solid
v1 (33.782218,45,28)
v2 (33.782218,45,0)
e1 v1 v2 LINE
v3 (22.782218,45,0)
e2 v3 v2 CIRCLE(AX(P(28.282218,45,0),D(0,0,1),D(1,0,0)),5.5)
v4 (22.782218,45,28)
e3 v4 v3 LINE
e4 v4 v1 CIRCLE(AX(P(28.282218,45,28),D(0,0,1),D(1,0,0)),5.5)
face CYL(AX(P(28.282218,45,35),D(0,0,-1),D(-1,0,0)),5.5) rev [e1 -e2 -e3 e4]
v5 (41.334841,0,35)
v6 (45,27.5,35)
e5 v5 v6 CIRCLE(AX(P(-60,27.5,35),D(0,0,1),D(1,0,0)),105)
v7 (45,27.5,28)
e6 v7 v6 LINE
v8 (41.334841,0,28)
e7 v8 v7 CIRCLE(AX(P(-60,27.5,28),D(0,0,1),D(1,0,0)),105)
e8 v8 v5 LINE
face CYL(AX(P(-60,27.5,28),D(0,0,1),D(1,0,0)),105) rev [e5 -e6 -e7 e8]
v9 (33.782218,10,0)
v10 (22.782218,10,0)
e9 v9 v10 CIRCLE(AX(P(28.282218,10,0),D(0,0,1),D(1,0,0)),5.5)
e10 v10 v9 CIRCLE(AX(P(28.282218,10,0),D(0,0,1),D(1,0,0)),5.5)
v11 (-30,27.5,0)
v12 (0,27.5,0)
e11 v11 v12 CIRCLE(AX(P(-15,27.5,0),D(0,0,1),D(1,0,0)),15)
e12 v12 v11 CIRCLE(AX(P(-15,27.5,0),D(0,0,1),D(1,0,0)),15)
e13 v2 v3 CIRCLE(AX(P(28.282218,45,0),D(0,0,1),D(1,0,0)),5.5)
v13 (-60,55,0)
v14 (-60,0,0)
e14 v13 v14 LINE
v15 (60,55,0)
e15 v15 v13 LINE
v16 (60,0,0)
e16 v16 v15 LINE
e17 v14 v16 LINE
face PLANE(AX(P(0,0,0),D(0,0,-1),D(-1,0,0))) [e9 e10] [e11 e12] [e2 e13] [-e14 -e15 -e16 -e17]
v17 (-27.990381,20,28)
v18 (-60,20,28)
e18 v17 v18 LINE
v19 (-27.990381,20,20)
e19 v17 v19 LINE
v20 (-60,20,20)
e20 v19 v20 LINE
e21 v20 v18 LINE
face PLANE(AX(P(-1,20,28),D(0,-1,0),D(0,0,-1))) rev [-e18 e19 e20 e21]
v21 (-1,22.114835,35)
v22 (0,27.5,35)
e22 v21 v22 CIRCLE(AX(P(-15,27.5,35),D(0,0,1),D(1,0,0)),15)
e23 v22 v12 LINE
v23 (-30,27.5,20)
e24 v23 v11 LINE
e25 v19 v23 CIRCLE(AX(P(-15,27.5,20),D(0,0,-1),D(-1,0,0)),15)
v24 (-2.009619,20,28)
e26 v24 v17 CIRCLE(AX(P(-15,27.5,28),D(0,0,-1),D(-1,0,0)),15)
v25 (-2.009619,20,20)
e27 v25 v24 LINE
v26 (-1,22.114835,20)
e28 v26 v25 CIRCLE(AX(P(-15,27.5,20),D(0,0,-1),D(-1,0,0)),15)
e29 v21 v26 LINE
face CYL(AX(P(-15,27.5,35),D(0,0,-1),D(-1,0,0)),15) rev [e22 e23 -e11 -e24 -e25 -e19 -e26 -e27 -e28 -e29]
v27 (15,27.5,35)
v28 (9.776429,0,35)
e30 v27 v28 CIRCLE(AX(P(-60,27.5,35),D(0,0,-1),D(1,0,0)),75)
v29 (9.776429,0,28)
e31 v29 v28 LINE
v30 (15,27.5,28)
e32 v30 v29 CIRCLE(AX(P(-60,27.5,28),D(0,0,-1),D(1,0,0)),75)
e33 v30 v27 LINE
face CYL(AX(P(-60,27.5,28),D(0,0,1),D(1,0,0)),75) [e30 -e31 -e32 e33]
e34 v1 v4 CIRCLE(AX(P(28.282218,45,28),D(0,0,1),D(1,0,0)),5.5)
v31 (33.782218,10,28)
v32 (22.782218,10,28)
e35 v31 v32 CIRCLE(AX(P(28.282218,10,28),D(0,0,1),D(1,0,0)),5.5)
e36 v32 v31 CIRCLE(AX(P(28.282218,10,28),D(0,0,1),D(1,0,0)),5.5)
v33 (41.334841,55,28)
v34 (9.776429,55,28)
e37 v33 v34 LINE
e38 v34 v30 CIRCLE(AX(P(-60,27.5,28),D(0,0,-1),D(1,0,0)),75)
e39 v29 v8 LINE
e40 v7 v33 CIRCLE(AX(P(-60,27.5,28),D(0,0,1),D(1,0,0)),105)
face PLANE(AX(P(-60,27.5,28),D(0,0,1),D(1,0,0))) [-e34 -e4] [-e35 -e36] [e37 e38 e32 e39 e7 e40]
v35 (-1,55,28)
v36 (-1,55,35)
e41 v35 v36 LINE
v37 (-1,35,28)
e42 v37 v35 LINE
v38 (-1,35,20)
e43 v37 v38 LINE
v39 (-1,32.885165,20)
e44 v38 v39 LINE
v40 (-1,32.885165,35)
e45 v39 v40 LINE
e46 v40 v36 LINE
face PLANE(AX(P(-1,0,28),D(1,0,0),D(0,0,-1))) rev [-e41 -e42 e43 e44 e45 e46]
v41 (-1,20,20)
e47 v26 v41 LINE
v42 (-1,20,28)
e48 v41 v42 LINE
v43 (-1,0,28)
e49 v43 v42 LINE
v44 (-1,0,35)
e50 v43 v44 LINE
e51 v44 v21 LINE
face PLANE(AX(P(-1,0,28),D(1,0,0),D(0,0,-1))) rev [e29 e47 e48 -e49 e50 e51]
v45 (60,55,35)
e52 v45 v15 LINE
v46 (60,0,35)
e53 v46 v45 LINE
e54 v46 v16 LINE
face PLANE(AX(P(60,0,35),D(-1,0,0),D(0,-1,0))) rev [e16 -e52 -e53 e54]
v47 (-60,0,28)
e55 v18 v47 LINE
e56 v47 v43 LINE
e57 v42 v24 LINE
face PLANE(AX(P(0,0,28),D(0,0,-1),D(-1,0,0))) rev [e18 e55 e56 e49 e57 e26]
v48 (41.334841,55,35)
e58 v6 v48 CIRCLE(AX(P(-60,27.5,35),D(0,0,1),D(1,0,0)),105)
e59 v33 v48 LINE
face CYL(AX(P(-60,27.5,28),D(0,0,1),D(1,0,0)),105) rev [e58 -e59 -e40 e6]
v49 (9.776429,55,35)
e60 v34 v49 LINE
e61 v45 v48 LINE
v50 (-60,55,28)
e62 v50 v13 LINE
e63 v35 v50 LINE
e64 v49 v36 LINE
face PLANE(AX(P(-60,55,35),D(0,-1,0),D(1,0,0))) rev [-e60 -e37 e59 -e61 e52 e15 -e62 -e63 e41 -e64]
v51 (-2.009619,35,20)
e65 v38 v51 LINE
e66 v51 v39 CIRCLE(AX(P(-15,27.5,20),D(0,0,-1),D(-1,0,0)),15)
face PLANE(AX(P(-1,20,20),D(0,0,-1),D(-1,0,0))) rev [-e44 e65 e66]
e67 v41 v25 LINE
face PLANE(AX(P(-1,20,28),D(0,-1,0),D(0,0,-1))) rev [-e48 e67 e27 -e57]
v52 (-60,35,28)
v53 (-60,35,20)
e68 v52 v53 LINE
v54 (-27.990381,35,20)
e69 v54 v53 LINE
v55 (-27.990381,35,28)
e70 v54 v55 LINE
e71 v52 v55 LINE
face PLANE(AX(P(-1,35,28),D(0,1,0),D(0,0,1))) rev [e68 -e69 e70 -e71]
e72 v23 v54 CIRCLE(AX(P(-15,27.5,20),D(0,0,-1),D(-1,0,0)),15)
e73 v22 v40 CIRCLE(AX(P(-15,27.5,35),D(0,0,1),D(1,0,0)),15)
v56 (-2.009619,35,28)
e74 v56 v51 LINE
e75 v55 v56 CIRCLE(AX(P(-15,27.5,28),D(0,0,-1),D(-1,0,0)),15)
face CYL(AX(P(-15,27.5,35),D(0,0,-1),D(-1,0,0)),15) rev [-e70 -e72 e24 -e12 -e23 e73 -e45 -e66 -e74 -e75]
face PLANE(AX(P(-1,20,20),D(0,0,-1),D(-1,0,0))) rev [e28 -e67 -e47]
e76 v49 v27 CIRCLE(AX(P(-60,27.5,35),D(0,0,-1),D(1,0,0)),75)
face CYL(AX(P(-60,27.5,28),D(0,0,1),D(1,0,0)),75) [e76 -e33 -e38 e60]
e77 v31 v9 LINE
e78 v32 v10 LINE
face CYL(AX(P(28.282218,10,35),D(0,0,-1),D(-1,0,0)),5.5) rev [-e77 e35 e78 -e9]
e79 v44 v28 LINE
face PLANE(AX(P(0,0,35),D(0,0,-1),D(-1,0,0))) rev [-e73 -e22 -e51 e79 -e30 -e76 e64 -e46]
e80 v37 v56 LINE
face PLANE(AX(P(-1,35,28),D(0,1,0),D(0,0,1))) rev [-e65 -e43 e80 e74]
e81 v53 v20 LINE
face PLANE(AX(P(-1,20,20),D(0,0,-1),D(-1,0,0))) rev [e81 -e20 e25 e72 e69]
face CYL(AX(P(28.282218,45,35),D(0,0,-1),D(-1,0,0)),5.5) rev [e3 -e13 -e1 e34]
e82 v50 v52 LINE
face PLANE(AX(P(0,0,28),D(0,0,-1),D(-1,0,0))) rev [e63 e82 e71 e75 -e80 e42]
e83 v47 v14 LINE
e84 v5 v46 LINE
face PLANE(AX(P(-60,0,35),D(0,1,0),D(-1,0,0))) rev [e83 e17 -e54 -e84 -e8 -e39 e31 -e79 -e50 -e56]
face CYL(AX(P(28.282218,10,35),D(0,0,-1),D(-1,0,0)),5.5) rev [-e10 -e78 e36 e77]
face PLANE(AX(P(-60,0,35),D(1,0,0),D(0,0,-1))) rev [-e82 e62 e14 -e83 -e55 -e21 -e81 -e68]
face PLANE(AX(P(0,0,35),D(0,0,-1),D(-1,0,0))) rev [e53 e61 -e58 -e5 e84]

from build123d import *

# Parameters (mm, degrees)
SLIDE_PROFILE_SKETCH_W   = 120
SLIDE_PROFILE_SKETCH_H   = 55
SLIDE_PROFILE_SKETCH_R   = 15
SLIDE_PROFILE_SKETCH_R_2 = 5.5
SLIDE_BODY_35MM_DEPTH    = 35
FACE_RECESS_7MM_DEPTH    = 7
CURVED_POCKET_SKETCH_W   = 59
CURVED_POCKET_SKETCH_H   = 55
CURVED_POCKET_7MM_DEPTH  = 7
THROUGH_CUT_SKETCH_W     = 8
THROUGH_CUT_SKETCH_H     = 15
THROUGH_CUT_59MM_DEPTH   = 59


with BuildPart() as part:
    # Slide Profile Sketch → Slide Body 35mm (new body)
    with BuildSketch(Plane.XY):
        with Locations((0, 27.5)):
            Rectangle(SLIDE_PROFILE_SKETCH_W, SLIDE_PROFILE_SKETCH_H)
        with Locations((-15, 27.5)):
            Circle(SLIDE_PROFILE_SKETCH_R, mode=Mode.SUBTRACT)
        with Locations((28.282217915, 45)):
            Circle(SLIDE_PROFILE_SKETCH_R_2, mode=Mode.SUBTRACT)
        with Locations((28.282217915, 10)):
            Circle(SLIDE_PROFILE_SKETCH_R_2, mode=Mode.SUBTRACT)
    extrude(amount=SLIDE_BODY_35MM_DEPTH)

    # Face Recess Sketch → Face Recess 7mm (cut)
    with BuildSketch(Plane.XY.offset(35)):
        with BuildLine():
            Line((9.776428685, 55), (41.334840998, 55))
            ThreePointArc((41.334840998, 55), (45, 27.5), (41.334840998, 0))
            Line((41.334840998, 0), (9.776428685, 0))
            ThreePointArc((9.776428685, 0), (15, 27.5), (9.776428685, 55))
        make_face()
    extrude(amount=-FACE_RECESS_7MM_DEPTH, mode=Mode.SUBTRACT)

    # Curved Pocket Sketch → Curved Pocket 7mm (cut)
    with BuildSketch(Plane.XY.offset(35)):
        with Locations((-30.5, 27.5)):
            Rectangle(CURVED_POCKET_SKETCH_W, CURVED_POCKET_SKETCH_H)
    extrude(amount=-CURVED_POCKET_7MM_DEPTH, mode=Mode.SUBTRACT)

    # Through Cut Sketch → Through Cut 59mm (cut)
    with BuildSketch(Plane.ZY.offset(60)):
        with Locations((24, 27.5)):
            Rectangle(THROUGH_CUT_SKETCH_W, THROUGH_CUT_SKETCH_H)
    extrude(amount=-THROUGH_CUT_59MM_DEPTH, mode=Mode.SUBTRACT)


solid = part.part
